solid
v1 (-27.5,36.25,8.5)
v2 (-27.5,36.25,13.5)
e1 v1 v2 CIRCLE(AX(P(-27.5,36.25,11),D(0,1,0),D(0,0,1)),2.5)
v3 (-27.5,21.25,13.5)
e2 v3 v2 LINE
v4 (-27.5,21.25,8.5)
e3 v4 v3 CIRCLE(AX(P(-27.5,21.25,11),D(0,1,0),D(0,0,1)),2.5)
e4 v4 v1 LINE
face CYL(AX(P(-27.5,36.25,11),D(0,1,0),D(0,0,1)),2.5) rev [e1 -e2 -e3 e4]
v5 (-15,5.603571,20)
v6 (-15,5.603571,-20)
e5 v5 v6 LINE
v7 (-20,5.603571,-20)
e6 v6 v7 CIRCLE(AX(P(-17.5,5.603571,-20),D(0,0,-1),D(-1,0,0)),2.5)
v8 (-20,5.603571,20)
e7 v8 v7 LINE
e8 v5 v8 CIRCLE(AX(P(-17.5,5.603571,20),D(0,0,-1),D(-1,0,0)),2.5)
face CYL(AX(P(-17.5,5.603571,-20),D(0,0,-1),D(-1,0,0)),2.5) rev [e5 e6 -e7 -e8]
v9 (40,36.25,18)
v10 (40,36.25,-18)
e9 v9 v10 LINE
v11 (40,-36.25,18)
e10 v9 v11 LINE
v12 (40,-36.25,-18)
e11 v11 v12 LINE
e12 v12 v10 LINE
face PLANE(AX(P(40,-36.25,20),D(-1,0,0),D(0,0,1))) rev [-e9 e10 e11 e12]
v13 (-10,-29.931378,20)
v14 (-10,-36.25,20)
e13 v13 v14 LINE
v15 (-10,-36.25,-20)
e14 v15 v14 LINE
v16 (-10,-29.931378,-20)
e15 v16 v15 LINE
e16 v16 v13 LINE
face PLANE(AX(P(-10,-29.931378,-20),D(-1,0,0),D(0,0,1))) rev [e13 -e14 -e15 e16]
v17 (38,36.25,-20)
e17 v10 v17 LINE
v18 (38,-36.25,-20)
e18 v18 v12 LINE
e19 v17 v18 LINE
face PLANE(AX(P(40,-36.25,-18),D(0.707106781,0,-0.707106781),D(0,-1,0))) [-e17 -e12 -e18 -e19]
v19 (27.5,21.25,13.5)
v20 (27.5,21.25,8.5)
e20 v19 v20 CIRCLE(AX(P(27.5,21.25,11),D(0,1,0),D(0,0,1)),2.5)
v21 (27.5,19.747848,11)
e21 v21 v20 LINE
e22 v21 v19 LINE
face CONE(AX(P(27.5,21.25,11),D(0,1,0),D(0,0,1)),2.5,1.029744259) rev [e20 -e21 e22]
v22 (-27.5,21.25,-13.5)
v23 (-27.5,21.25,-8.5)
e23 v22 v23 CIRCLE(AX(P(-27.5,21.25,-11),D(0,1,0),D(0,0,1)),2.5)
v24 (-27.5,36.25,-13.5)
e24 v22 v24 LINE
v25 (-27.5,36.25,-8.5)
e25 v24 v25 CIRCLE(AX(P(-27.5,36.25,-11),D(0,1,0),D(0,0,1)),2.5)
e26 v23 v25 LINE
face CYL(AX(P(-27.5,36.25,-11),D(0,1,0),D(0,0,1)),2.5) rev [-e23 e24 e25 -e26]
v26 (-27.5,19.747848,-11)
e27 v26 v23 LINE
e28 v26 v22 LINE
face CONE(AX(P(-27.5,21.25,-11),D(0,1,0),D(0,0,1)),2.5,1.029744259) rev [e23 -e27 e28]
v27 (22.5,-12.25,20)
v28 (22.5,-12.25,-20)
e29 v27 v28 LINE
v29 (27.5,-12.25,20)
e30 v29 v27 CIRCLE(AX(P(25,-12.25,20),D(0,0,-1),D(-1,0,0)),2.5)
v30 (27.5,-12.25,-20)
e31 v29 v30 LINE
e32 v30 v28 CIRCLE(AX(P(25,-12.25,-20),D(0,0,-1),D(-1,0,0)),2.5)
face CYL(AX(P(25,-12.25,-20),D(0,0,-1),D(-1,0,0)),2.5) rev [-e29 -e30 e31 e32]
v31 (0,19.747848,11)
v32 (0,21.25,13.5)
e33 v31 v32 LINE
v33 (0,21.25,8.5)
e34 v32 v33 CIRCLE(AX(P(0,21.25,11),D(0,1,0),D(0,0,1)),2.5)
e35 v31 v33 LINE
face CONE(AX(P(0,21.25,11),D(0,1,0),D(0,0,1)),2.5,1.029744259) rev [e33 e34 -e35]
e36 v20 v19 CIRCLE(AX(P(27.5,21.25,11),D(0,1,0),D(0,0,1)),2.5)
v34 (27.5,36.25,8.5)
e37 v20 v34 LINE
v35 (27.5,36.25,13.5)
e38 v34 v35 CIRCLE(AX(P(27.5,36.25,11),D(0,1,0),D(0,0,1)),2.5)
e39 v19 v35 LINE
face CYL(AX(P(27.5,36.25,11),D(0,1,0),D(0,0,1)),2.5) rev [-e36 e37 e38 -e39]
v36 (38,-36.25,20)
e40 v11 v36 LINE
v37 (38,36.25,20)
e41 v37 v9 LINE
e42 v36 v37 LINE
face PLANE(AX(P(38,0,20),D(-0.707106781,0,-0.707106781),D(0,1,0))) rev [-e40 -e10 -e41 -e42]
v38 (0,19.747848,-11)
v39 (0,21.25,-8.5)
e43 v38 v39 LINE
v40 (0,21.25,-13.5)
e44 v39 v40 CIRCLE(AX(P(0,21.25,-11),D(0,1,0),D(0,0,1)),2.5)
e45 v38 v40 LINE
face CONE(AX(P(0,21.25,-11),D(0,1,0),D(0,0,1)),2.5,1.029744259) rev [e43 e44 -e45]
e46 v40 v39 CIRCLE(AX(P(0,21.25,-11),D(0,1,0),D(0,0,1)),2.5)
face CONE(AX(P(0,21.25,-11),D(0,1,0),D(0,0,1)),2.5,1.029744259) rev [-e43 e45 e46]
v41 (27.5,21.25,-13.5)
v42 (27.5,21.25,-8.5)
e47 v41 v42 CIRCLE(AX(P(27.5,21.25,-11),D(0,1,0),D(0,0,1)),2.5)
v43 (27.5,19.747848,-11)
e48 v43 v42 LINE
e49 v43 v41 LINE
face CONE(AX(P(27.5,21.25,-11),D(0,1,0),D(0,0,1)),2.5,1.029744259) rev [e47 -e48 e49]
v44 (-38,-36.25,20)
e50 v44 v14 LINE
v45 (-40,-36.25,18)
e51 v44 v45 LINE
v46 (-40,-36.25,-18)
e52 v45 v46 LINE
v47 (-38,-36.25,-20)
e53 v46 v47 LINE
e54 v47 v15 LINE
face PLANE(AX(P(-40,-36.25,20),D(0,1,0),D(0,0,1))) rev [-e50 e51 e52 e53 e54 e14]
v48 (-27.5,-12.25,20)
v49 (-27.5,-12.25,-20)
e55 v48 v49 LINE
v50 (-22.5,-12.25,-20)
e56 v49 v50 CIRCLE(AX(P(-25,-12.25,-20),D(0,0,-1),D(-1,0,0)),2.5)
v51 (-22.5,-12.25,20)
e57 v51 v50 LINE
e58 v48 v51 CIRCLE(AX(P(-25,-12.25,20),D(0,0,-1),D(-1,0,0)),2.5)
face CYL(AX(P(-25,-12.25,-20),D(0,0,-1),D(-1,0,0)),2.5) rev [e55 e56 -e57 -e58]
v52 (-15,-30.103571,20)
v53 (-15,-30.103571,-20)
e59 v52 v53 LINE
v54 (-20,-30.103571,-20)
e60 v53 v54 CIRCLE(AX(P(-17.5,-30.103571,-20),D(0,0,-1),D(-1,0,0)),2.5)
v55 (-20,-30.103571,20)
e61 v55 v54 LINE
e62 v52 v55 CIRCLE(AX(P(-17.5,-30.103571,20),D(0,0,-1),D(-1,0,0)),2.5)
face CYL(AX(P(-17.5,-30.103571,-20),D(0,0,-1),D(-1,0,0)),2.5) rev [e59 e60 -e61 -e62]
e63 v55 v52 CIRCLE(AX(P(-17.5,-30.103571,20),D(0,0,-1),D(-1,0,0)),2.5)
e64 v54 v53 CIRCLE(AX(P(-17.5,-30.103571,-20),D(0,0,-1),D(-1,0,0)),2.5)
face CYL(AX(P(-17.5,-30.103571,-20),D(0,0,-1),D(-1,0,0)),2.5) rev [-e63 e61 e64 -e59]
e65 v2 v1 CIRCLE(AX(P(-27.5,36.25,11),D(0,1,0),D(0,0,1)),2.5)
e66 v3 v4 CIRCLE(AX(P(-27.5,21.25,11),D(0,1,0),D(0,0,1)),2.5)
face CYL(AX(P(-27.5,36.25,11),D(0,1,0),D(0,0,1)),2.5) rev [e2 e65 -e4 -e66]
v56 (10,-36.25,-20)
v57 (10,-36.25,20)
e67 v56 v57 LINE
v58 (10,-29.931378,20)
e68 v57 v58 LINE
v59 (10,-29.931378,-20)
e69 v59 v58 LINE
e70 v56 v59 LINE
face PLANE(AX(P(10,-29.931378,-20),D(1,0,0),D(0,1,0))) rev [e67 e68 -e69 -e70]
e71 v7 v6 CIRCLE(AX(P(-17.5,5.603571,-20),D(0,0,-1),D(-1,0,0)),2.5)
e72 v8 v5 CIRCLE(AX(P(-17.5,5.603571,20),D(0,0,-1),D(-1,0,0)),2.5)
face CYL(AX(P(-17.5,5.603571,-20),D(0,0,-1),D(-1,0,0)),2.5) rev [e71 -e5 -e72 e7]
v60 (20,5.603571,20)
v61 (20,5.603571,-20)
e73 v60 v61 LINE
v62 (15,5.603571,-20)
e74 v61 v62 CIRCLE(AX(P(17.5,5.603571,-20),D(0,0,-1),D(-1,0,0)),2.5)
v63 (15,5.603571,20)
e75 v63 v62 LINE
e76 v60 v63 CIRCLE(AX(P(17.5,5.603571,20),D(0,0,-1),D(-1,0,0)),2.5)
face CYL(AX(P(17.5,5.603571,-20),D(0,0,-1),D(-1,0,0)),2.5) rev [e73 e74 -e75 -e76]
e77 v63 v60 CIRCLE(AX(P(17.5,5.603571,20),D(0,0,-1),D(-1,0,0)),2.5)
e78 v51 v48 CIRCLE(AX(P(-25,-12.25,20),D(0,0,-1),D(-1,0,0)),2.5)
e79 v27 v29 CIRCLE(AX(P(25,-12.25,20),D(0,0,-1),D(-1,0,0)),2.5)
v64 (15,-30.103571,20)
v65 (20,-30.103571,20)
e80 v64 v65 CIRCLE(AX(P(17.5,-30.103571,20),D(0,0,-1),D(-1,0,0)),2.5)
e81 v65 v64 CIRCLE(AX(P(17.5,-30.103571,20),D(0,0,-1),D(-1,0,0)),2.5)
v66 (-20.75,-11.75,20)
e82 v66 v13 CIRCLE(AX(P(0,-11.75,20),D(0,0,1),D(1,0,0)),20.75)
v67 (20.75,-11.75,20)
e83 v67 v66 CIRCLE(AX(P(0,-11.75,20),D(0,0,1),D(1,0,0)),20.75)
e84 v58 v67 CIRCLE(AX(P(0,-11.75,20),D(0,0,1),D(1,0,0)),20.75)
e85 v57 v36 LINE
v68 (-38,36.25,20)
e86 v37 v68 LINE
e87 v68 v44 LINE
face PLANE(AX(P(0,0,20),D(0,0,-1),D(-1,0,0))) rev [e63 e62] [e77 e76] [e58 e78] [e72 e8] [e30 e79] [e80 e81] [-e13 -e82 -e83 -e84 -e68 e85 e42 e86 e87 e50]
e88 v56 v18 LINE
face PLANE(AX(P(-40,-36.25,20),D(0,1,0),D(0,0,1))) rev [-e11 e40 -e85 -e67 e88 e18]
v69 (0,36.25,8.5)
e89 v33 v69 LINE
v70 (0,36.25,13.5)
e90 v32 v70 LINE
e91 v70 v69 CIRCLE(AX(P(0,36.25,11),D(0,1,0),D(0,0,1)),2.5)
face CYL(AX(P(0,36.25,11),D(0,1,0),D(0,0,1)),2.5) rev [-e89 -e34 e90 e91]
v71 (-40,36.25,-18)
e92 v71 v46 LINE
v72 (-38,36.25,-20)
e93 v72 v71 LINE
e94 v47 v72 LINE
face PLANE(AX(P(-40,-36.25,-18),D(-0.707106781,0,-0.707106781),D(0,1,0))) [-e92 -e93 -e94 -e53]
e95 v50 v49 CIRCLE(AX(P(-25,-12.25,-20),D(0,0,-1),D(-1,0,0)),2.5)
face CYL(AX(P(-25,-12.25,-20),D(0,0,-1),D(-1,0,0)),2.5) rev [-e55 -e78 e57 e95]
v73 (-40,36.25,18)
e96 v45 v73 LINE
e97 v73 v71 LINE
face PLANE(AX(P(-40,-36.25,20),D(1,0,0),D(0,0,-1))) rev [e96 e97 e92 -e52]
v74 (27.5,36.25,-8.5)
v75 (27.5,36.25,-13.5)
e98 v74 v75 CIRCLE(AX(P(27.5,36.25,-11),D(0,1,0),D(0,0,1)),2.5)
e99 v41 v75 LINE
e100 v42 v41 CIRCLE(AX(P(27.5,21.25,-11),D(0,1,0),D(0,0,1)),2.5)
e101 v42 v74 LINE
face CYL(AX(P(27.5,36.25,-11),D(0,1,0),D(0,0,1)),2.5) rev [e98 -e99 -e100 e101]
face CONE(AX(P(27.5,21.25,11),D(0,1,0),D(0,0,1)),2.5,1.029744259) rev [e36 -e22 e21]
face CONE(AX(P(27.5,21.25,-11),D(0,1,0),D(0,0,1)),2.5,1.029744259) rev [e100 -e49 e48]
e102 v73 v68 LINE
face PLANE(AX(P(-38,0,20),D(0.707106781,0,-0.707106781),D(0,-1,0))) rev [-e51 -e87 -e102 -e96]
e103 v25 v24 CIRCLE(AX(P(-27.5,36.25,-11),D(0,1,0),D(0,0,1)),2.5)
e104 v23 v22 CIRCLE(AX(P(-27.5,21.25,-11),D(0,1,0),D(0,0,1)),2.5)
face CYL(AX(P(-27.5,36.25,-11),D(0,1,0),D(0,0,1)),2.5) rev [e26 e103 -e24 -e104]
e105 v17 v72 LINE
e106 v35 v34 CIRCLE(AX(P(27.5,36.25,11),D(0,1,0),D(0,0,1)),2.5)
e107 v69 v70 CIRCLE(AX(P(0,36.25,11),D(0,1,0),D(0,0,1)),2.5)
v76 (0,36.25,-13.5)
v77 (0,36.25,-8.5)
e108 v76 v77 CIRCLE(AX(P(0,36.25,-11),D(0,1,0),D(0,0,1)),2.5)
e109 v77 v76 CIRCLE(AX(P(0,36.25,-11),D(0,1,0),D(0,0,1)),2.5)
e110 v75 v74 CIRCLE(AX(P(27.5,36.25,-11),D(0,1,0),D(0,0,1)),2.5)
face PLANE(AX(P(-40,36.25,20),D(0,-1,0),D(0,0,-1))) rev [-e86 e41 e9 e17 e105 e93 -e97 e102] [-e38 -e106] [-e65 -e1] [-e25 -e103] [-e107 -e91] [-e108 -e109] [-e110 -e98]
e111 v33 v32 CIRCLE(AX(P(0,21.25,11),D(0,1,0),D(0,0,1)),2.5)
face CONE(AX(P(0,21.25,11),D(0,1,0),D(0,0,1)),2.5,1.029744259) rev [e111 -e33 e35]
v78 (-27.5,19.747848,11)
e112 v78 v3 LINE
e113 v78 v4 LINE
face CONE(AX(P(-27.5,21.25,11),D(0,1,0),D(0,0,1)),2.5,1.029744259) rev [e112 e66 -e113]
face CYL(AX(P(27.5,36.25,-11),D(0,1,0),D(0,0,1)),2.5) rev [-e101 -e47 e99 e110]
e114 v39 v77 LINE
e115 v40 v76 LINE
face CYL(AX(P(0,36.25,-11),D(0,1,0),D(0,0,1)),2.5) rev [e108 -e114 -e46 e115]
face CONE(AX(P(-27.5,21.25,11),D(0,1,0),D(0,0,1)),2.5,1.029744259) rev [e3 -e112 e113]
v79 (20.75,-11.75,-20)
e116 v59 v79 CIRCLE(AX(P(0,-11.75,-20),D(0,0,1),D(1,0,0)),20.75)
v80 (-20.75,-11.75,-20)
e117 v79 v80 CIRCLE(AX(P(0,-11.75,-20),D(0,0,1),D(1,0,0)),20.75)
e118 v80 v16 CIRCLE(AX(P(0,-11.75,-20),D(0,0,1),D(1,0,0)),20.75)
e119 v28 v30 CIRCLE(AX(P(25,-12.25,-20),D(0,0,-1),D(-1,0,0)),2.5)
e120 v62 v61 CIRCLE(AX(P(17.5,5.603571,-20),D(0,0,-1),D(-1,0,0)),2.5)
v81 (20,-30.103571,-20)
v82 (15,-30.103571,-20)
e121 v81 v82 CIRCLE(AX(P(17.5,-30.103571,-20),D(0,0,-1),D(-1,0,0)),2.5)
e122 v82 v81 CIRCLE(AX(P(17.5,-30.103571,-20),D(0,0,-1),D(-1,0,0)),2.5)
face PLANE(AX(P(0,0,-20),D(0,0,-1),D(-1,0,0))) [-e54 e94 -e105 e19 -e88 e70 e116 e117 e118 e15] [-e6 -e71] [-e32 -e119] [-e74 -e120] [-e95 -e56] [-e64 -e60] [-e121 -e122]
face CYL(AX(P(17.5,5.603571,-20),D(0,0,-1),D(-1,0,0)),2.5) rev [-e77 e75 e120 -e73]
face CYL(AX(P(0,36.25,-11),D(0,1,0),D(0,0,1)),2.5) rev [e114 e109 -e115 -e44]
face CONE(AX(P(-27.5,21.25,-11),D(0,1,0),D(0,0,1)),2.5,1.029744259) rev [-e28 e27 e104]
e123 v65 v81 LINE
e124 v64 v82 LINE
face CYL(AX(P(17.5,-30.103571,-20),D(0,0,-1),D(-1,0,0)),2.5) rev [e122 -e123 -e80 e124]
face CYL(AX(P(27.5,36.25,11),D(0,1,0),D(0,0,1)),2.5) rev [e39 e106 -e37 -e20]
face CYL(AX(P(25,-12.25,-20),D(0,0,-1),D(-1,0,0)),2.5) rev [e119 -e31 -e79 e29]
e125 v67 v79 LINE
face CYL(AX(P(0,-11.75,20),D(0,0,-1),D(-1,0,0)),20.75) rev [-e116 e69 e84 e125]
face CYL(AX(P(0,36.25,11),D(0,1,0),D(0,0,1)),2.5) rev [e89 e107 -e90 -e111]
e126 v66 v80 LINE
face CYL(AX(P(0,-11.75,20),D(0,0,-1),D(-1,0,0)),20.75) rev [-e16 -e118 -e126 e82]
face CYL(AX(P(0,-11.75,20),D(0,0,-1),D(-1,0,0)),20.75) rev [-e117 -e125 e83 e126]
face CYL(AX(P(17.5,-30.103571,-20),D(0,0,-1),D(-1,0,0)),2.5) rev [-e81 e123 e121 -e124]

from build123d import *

# Parameters (mm, degrees)
SKETCH_1_W             = 80
SKETCH_1_H             = 72.5
SKETCH_1_R             = 20.75
EXTRUDE_1_DEPTH        = 20
SKETCH_2_W             = 20
SKETCH_2_H             = 6.318622164
CUT_EXTRUDE_1_DEPTH    = 68.186773252
HOLE_WIZARD_M6_1_D     = 5
HOLE_WIZARD_M6_2_D     = 5
HOLE_WIZARD_M6_2_DEPTH = 15
HOLE_WIZARD_M6_2_TIP   = 1.502151548
CHAMFER_1_SIZE         = 2


with BuildPart() as part:
    # 草图1 → 凸台-拉伸1 (new, symmetric)
    with BuildSketch(Plane.XY):
        Rectangle(SKETCH_1_W, SKETCH_1_H)
        with Locations((0, -11.75)):
            Circle(SKETCH_1_R, mode=Mode.SUBTRACT)
    extrude(amount=EXTRUDE_1_DEPTH, both=True)

    # 草图2 → 切除-拉伸1 (cut, through all)
    with BuildSketch(Plane.XY.offset(20)):
        with Locations((0, -33.090688918)):
            Rectangle(SKETCH_2_W, SKETCH_2_H)
    extrude(amount=-CUT_EXTRUDE_1_DEPTH, mode=Mode.SUBTRACT)

    # M6 螺纹孔1 (through all)
    with Locations(Plane(origin=(0, 0, -20), x_dir=(-1, 0, 0), z_dir=(0, 0, -1))):
        with Locations((-17.5, 5.603571071), (17.5, 5.603571071), (17.5, -30.103571071), (-17.5, -30.103571071), (-25, -12.25), (25, -12.25)):
            Hole(HOLE_WIZARD_M6_1_D / 2)

    # M6 螺纹孔2
    with Locations(Plane(origin=(0, 36.25, 0), x_dir=(1, 0, 0), z_dir=(0, 1, 0))):
        with Locations((-27.5, 11), (-27.5, -11), (27.5, -11), (27.5, 11), (0, 11), (0, -11)):
            Hole(HOLE_WIZARD_M6_2_D / 2, depth=HOLE_WIZARD_M6_2_DEPTH)
            with Locations((0, 0, -(HOLE_WIZARD_M6_2_DEPTH + HOLE_WIZARD_M6_2_TIP / 2))):  # 118° drill point
                Cone(0, HOLE_WIZARD_M6_2_D / 2, HOLE_WIZARD_M6_2_TIP, mode=Mode.SUBTRACT)

    # 倒角1
    chamfer_1_edges = [part.edges().sort_by_distance(p)[0] for p in [
        (-40, 0, 20),
        (40, 0, 20),
        (-40, 0, -20),
        (40, 0, -20),
    ]]
    chamfer(chamfer_1_edges, length=CHAMFER_1_SIZE)


solid = part.part
